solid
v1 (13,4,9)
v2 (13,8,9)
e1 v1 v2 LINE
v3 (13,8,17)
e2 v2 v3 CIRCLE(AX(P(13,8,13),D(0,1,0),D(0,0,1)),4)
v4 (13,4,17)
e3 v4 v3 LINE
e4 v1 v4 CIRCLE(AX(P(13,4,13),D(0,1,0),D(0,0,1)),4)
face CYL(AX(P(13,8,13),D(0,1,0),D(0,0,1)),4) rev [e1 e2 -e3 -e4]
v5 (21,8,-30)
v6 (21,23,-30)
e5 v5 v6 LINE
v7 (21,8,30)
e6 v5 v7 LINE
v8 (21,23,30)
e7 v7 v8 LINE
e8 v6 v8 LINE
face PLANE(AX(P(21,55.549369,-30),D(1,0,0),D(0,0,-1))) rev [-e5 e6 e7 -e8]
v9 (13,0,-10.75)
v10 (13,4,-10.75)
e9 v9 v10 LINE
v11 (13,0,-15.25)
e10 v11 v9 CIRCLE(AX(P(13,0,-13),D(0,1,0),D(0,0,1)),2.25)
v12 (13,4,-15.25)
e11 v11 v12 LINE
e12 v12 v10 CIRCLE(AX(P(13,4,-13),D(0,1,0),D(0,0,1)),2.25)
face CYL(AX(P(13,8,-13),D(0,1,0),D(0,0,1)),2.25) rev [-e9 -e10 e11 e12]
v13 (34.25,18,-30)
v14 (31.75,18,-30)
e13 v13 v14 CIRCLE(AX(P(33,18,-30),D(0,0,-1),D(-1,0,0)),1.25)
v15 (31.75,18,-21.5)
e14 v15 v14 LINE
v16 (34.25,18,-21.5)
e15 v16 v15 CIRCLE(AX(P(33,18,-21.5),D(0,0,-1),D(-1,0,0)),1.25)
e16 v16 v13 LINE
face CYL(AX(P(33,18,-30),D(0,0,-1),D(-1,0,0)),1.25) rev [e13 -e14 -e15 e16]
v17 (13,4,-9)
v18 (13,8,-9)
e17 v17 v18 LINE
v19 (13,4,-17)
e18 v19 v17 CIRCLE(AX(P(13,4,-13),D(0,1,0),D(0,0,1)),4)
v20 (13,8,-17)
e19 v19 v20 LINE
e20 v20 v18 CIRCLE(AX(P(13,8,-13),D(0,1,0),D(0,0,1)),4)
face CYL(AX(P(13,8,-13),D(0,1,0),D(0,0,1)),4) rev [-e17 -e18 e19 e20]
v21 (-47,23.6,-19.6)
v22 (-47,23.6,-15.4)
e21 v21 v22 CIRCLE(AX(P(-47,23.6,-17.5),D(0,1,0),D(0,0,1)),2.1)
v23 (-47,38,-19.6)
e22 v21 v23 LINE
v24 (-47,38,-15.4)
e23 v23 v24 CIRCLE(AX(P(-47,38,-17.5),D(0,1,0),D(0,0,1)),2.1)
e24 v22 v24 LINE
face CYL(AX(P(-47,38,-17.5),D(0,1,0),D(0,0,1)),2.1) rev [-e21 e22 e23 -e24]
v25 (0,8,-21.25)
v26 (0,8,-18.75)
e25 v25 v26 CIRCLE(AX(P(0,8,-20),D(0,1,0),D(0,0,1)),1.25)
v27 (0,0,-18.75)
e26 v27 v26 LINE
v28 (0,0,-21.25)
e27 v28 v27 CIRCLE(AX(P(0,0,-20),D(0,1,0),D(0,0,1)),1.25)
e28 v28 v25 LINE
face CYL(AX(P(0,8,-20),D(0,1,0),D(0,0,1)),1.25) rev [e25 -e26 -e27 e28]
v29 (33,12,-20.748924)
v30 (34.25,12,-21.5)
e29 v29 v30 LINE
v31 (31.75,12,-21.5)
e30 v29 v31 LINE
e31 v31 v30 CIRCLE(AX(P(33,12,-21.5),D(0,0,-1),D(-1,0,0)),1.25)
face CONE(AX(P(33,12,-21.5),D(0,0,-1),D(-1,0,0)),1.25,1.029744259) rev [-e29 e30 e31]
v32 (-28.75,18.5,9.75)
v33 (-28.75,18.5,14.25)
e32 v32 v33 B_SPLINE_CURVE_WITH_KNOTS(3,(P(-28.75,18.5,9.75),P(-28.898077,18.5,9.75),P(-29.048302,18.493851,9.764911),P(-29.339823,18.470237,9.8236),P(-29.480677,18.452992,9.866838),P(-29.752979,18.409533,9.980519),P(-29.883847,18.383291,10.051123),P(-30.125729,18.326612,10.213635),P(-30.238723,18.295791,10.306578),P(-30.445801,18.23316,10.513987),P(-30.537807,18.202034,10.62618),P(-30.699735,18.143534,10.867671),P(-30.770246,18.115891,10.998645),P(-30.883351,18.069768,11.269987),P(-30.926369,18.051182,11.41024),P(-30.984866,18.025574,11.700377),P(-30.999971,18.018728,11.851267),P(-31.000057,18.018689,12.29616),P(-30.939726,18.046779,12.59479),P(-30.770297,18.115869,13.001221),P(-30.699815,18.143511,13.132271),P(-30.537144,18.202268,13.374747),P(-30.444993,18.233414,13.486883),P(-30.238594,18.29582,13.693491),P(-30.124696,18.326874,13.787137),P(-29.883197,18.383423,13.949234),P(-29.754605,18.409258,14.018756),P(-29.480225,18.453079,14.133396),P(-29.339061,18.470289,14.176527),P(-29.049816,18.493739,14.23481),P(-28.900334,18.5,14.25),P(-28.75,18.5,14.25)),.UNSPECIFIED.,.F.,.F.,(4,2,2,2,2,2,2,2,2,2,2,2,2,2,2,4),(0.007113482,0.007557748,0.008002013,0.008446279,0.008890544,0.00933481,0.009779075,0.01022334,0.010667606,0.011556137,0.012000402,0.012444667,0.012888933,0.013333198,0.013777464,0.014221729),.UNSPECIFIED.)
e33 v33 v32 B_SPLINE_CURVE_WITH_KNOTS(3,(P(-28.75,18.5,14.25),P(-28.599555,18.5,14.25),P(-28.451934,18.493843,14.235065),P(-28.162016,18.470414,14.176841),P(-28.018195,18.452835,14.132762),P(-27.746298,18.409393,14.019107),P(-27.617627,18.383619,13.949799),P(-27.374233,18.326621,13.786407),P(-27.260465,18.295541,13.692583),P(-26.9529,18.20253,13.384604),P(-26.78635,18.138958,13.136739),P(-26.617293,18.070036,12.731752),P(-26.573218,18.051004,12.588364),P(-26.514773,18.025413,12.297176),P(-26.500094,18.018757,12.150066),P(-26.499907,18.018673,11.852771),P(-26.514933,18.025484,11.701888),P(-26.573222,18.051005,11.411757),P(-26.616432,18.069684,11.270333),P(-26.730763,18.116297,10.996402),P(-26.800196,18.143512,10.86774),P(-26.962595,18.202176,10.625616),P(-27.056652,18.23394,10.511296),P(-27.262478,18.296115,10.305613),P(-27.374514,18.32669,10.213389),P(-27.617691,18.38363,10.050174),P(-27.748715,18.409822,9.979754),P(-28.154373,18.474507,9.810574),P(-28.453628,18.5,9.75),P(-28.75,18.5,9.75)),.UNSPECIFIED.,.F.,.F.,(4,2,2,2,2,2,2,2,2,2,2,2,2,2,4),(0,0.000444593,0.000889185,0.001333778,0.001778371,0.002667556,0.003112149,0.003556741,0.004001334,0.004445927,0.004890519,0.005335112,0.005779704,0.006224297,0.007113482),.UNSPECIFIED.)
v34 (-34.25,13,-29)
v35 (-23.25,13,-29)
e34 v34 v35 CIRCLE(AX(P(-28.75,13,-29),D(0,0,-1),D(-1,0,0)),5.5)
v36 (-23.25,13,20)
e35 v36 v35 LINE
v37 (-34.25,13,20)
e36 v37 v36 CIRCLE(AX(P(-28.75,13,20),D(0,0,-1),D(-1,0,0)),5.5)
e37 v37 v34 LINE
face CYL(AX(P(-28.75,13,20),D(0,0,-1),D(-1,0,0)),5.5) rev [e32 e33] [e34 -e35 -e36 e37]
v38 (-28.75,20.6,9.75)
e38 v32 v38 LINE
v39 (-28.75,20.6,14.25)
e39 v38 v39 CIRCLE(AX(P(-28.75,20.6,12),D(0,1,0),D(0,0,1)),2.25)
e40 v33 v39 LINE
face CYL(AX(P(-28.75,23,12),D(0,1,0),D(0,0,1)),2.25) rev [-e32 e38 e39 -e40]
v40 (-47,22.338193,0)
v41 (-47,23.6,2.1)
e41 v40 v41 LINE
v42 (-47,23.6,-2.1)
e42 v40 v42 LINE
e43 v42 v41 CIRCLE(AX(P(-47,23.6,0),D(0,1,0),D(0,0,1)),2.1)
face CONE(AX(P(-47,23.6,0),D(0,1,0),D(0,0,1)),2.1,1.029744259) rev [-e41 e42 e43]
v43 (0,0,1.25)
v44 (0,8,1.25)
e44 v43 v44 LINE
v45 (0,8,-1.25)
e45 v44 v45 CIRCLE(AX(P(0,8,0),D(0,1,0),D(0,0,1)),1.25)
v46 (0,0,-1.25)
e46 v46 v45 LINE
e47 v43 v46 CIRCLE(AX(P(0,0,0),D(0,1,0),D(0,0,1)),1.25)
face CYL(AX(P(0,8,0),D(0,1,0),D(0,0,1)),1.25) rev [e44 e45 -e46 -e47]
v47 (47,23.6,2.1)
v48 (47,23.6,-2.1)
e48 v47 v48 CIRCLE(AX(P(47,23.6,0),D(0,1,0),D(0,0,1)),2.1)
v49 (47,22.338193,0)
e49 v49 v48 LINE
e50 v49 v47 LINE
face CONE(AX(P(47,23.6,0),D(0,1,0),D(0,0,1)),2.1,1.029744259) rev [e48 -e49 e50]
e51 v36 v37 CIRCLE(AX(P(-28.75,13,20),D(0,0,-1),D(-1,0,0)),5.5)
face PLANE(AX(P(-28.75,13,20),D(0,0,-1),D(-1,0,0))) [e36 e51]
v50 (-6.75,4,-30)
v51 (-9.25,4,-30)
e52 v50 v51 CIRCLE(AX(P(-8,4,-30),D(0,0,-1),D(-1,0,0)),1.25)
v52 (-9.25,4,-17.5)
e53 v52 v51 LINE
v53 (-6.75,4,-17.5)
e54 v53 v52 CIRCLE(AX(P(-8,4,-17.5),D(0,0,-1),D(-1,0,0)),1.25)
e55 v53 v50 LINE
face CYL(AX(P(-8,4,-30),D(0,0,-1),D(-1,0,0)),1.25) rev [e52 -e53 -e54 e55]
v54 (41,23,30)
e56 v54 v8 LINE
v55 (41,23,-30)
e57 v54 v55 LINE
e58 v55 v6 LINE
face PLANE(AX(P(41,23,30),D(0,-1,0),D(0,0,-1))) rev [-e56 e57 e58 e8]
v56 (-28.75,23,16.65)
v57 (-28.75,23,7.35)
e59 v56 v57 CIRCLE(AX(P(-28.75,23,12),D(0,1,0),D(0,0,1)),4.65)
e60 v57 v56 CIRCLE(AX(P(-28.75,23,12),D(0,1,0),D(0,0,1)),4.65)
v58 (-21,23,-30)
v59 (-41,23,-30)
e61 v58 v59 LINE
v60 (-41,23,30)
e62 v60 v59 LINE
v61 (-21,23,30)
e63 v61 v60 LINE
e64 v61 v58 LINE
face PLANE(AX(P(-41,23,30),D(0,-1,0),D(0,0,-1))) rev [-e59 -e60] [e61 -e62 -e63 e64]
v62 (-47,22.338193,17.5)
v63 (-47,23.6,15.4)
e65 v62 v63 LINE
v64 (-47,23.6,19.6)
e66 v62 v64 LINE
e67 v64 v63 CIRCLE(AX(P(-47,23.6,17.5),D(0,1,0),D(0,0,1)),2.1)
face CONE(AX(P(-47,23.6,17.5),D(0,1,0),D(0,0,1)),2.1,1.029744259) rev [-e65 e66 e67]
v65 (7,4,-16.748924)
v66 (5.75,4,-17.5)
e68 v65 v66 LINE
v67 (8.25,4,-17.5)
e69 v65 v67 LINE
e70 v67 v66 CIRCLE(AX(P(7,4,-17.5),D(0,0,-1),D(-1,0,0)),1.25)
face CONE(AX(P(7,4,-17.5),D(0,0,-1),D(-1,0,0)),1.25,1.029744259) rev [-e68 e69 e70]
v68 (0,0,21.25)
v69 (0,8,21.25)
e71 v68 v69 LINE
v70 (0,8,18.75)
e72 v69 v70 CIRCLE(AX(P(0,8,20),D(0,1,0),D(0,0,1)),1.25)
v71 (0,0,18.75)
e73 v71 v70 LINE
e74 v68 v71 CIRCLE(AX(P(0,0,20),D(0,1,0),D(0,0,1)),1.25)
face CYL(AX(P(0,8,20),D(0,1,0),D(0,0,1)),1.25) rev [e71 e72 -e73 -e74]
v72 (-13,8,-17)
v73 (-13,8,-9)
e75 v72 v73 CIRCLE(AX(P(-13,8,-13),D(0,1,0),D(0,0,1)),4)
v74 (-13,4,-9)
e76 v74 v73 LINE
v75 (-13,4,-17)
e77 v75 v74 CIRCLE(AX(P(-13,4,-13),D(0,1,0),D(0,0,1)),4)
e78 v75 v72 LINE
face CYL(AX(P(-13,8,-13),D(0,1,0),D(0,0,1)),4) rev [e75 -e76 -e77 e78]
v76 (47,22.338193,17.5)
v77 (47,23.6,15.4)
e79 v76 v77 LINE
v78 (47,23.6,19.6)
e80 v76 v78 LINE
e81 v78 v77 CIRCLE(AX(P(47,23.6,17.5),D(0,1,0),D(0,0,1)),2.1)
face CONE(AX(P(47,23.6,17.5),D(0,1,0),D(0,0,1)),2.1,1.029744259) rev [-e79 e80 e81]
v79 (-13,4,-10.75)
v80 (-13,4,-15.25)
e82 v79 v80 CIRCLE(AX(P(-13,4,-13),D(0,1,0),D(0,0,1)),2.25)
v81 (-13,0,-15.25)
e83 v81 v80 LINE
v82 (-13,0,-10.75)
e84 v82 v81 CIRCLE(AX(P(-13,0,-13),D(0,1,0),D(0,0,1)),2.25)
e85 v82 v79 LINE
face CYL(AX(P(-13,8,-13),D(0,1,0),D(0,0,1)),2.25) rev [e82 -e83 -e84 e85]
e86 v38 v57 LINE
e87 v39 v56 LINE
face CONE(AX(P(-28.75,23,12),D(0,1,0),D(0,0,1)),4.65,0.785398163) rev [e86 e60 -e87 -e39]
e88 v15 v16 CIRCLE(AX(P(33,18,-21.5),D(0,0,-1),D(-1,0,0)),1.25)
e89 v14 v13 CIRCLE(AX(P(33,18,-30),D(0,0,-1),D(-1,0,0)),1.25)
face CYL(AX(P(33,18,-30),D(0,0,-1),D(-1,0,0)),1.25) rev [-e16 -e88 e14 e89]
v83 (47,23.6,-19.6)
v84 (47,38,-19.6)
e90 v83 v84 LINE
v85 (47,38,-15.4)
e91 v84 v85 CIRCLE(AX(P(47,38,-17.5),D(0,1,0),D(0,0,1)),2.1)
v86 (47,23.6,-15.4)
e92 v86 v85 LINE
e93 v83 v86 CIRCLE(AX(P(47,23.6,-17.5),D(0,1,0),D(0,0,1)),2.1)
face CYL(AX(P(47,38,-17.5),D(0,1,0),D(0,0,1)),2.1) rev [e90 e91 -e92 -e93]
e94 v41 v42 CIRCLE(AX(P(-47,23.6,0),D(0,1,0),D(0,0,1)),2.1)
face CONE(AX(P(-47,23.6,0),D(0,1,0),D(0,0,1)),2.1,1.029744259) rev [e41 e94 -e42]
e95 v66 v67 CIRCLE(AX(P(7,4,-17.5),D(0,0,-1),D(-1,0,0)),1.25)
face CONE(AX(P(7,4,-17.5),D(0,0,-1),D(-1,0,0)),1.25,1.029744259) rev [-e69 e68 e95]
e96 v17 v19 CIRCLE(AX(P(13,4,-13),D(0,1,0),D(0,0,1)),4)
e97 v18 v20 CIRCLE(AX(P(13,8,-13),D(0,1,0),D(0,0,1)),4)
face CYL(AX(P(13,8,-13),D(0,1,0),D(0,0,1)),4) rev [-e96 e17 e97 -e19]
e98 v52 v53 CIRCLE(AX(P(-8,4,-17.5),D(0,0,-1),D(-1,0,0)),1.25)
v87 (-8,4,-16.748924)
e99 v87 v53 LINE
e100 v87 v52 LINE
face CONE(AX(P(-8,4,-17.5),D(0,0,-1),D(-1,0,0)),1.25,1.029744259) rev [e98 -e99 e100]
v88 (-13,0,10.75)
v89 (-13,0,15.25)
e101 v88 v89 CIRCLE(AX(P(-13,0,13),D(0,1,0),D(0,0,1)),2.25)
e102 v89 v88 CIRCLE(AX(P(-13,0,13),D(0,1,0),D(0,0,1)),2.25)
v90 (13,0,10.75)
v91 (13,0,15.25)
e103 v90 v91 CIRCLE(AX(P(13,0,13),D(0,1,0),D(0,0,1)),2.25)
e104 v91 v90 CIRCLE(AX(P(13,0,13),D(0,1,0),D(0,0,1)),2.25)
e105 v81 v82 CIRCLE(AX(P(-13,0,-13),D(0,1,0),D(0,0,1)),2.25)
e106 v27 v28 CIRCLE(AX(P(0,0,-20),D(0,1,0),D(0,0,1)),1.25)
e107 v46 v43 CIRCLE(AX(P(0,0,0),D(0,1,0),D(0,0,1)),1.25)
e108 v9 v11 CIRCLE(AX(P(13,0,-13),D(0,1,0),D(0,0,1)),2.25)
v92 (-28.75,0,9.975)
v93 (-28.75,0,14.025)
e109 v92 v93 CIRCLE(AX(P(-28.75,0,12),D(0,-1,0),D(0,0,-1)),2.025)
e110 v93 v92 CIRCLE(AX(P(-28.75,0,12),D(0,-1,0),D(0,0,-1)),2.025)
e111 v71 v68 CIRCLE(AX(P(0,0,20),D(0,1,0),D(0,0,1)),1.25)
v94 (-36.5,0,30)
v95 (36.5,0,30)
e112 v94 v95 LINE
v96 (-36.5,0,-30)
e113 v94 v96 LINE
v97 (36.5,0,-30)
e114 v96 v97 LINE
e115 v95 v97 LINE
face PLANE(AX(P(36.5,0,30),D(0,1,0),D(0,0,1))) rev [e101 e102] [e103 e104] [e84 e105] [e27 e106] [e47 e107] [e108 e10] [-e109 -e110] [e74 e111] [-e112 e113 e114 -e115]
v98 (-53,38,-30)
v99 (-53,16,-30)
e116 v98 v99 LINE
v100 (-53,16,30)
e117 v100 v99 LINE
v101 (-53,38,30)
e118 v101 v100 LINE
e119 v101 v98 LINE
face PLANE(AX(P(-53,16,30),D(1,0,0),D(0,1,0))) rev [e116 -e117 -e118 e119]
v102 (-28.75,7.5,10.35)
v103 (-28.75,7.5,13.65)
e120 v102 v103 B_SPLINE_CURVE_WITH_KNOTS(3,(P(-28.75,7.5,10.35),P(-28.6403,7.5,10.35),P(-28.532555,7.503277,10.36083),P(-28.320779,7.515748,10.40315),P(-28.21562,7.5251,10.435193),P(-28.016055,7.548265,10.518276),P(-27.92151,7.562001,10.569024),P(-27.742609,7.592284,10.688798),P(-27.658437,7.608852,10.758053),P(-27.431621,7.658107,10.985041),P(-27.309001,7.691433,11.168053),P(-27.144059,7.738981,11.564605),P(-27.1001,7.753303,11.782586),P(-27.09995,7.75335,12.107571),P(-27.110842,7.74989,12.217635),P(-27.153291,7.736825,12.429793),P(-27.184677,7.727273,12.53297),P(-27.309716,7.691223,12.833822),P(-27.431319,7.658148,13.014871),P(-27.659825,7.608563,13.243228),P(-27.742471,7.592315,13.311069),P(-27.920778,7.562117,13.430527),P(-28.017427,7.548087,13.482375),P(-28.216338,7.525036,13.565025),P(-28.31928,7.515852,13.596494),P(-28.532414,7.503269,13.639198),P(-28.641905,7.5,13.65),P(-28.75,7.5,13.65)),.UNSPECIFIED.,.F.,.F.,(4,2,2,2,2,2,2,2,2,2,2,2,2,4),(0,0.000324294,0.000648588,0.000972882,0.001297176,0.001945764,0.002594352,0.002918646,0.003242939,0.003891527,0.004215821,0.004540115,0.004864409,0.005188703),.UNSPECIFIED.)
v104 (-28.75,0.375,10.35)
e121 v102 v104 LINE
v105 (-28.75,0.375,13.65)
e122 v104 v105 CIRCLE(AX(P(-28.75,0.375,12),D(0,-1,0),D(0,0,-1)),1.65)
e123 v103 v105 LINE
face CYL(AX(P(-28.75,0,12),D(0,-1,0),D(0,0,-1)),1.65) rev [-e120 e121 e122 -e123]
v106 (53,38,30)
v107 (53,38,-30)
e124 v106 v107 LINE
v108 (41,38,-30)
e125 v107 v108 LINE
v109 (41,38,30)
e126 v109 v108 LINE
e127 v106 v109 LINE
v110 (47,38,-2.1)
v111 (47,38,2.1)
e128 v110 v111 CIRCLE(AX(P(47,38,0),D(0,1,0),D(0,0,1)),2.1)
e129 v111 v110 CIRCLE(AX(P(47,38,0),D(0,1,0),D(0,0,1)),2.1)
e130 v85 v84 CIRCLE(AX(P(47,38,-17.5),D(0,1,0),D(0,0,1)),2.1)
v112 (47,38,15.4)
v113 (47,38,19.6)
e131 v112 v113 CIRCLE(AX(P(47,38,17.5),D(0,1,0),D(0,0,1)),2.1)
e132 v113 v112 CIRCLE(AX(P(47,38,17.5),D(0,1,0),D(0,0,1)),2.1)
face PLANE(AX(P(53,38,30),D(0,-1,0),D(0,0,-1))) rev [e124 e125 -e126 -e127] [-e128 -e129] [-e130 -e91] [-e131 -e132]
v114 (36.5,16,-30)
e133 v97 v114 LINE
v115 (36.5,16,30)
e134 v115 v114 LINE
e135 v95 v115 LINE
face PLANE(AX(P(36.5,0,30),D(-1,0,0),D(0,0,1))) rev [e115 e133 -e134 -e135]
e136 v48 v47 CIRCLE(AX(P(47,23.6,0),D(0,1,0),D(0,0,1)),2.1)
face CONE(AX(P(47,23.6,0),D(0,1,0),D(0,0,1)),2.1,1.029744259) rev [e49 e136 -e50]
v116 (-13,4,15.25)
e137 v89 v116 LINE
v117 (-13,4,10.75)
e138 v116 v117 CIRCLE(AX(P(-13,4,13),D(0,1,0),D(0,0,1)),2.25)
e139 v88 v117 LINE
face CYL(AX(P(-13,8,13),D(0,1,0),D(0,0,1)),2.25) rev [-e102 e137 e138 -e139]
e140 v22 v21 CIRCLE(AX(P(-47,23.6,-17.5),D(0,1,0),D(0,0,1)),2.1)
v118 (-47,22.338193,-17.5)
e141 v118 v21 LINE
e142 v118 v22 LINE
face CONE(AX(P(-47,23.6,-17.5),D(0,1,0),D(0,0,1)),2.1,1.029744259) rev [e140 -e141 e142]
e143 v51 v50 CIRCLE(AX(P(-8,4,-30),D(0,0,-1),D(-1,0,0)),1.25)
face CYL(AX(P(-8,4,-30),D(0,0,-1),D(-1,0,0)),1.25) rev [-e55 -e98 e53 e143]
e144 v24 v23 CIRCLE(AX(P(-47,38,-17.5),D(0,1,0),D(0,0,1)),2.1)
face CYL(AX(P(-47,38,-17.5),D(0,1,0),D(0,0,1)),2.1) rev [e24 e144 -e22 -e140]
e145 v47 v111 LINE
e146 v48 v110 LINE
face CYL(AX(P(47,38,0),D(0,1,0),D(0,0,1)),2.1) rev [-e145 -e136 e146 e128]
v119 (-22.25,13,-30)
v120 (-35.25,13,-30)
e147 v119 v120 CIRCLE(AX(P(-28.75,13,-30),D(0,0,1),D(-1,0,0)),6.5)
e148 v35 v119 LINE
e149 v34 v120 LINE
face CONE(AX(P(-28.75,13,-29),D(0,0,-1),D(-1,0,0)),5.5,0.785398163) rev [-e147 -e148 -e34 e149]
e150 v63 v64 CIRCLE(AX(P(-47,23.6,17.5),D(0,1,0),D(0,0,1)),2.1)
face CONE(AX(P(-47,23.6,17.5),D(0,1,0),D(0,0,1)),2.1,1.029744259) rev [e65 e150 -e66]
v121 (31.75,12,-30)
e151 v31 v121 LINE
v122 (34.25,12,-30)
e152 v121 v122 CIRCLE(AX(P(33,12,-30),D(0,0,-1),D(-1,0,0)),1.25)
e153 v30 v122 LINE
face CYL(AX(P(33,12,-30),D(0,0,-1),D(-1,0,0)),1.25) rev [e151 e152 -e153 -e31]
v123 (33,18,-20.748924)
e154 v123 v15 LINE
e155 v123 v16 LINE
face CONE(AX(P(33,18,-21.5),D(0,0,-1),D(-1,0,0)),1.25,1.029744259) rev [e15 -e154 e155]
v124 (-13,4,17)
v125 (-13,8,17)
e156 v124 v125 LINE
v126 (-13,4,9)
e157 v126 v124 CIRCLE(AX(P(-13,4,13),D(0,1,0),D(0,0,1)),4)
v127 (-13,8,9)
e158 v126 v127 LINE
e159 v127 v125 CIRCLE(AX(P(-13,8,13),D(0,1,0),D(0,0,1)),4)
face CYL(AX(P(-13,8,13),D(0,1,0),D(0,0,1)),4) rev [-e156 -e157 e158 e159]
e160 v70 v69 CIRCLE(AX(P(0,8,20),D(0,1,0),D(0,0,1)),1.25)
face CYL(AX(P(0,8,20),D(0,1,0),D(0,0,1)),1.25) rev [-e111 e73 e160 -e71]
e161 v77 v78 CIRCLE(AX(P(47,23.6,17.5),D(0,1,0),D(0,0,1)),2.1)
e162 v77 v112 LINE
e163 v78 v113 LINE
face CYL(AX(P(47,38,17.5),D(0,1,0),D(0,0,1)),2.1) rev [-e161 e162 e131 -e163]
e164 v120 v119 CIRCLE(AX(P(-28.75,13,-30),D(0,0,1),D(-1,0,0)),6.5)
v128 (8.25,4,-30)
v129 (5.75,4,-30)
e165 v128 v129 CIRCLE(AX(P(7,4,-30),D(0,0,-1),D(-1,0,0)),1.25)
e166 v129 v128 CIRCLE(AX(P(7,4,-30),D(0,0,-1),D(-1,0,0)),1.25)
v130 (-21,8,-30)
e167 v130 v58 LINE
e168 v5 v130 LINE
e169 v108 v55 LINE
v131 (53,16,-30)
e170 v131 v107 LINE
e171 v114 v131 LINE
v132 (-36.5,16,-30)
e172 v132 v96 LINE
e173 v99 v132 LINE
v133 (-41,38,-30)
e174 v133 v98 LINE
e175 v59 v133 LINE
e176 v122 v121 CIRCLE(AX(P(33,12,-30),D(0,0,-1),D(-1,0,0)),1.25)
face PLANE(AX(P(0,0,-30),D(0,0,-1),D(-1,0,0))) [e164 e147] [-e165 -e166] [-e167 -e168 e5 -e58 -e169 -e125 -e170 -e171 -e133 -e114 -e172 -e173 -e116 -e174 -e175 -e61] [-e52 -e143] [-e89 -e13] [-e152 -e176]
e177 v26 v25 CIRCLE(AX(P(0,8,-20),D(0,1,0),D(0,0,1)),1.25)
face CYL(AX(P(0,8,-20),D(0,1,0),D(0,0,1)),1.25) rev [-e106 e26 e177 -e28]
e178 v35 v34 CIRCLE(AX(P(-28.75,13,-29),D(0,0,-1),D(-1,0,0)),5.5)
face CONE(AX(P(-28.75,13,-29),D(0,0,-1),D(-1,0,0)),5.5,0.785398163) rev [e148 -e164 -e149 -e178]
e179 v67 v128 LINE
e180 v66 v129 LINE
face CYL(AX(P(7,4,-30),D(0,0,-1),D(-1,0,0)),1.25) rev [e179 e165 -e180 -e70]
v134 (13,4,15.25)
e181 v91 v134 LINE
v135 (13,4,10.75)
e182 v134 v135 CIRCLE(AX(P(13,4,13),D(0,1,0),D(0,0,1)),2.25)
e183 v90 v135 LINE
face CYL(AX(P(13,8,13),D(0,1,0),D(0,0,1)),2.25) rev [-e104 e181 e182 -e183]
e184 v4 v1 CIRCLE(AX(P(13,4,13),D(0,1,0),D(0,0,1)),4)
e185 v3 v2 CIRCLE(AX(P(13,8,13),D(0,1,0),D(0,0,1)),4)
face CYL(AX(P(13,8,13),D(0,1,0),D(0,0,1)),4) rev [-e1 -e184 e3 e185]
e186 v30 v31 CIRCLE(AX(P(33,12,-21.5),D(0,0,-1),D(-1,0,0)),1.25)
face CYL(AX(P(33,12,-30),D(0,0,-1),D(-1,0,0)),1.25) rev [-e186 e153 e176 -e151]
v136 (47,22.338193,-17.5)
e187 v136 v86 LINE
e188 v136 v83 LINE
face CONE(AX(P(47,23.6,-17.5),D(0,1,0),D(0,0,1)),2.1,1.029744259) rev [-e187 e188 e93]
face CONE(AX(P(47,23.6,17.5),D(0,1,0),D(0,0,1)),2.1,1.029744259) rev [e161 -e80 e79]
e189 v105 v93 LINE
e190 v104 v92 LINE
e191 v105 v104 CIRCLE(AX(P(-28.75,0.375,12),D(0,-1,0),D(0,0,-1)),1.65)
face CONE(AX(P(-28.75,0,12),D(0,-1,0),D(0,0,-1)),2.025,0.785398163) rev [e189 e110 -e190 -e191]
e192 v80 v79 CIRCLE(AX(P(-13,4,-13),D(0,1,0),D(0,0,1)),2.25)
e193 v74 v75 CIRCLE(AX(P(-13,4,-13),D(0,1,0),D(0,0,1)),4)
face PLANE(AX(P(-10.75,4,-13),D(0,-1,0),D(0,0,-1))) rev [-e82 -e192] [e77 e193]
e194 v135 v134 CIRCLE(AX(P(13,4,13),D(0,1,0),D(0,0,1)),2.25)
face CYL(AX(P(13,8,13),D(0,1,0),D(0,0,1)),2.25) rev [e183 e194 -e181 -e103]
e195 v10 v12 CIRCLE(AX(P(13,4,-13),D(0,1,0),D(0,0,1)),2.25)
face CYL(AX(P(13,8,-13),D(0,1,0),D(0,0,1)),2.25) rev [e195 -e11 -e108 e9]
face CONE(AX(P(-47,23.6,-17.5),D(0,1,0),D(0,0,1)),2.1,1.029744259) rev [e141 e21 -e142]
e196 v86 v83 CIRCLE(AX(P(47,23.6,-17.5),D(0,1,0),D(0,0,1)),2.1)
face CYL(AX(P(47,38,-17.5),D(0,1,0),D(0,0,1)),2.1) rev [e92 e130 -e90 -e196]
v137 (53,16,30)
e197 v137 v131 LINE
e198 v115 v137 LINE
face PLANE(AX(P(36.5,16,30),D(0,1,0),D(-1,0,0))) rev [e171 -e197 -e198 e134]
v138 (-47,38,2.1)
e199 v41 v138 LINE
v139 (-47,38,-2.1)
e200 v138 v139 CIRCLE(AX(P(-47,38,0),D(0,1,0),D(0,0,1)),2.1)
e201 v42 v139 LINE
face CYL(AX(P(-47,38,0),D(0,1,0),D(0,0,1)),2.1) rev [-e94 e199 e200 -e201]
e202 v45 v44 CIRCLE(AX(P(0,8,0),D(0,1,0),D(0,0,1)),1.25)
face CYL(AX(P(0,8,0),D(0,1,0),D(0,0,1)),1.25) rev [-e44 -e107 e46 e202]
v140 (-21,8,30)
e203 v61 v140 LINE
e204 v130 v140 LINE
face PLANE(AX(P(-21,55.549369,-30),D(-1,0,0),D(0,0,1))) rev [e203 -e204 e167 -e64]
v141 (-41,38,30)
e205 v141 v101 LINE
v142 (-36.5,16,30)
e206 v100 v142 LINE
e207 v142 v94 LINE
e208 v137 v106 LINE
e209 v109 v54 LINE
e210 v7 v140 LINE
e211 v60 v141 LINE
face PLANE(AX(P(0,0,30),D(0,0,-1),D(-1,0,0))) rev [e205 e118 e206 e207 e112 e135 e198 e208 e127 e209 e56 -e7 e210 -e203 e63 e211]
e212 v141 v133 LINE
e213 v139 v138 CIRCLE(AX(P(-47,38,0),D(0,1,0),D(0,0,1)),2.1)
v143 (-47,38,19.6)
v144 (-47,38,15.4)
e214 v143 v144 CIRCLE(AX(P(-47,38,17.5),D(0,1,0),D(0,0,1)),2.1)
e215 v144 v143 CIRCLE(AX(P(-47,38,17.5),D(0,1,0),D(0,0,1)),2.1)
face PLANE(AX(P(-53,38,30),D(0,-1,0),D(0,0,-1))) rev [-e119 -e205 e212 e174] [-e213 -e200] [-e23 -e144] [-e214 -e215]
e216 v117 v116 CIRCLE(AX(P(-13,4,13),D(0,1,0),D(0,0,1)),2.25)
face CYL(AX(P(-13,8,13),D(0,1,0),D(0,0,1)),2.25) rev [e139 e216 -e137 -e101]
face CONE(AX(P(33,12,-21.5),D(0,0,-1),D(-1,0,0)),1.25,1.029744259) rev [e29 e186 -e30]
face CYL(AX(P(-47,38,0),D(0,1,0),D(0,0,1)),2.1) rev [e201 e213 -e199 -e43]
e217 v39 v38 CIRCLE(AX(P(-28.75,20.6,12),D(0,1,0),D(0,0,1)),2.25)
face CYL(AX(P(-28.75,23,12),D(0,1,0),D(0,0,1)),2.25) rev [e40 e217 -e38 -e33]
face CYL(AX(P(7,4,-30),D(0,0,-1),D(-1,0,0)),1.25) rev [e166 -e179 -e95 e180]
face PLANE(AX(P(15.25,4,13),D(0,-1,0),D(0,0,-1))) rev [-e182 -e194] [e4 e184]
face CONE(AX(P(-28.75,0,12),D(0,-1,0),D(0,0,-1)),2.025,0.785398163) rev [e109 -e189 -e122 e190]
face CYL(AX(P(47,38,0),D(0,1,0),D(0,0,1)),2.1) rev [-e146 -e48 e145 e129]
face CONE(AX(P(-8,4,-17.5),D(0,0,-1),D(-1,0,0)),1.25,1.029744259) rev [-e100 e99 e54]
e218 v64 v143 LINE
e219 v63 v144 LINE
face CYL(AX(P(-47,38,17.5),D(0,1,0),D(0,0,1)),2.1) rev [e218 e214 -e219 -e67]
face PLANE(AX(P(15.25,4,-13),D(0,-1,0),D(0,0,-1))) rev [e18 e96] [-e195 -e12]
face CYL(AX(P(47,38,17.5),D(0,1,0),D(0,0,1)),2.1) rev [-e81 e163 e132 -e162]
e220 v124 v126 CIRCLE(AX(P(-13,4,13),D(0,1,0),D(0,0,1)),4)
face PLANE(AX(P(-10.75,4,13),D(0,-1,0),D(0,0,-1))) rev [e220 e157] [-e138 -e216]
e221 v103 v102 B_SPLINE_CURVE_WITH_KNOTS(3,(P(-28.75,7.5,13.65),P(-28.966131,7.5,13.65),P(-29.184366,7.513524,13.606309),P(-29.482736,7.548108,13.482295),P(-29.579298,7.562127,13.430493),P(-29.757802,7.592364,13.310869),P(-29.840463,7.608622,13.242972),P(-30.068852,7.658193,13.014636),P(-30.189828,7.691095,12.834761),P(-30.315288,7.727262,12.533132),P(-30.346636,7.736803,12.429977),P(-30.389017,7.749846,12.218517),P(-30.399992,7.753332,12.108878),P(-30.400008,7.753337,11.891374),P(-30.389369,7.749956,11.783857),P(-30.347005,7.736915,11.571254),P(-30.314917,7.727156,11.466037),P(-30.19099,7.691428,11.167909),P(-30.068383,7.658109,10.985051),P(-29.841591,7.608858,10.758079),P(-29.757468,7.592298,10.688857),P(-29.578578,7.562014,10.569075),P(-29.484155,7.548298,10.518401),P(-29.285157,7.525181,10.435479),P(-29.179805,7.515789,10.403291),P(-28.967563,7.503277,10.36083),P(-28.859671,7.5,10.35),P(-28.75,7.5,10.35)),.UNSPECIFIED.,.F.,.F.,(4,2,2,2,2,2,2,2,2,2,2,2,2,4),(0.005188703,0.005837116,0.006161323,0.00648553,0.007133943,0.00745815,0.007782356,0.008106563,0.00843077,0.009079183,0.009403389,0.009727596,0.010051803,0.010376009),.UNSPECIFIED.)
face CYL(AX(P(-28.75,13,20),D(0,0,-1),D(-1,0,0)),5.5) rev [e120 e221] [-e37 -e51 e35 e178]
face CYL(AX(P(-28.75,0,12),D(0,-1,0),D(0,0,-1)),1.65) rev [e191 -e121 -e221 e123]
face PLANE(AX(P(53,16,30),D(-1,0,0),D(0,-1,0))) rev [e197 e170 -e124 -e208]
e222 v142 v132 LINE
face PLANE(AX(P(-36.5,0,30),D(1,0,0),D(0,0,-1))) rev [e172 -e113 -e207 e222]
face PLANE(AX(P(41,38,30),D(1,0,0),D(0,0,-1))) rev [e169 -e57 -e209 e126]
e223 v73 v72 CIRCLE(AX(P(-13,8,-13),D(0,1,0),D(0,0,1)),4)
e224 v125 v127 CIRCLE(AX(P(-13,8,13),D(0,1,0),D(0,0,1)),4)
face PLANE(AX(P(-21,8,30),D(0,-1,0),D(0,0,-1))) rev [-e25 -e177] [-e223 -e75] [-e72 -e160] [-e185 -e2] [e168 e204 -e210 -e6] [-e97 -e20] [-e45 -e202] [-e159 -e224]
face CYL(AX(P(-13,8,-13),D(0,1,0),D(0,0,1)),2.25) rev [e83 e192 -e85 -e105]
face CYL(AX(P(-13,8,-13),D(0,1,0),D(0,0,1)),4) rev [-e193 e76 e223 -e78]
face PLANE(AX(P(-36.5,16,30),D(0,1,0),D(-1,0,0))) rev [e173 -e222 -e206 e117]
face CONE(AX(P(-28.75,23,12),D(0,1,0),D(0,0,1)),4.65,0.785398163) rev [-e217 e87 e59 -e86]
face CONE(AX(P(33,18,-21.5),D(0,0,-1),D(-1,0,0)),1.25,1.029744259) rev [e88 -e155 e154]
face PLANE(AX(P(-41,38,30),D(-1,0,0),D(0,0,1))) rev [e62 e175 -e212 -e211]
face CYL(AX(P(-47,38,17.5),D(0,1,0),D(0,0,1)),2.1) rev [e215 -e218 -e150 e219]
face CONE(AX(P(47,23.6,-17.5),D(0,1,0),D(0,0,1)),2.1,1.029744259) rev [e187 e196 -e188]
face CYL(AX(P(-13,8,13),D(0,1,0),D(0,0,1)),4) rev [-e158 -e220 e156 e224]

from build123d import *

# Parameters (mm, degrees)
EXTRUDE_1_DEPTH              = 30
HOLE_WIZARD_M5_1_AT_2_COUNT  = 2
HOLE_WIZARD_M5_1_AT_2_PITCH  = 35
HOLE_WIZARD_M5_1_AT_3_COUNT  = 2
HOLE_WIZARD_M5_1_AT_3_PITCH  = 17.5
SKETCH_15_W                  = 50
SKETCH_15_H                  = 47.549368588
CUT_EXTRUDE_7_DEPTH          = 89.617154096
HOLE_WIZARD_2_D              = 4.5
HOLE_WIZARD_2_CBORE_D        = 8
HOLE_WIZARD_2_CBORE_DEPTH    = 4
HOLE_WIZARD_M3_4_D           = 2.5
HOLE_WIZARD_M3_4_DEPTH       = 12.5
HOLE_WIZARD_M3_4_TIP         = 0.751075774
HOLE_WIZARD_M3_5_D           = 2.5
PATTERN_LINEAR_1_COUNT       = 3
PATTERN_LINEAR_1_PITCH       = 20
HOLE_WIZARD_M3_6_D           = 2.5
HOLE_WIZARD_M3_6_DEPTH       = 8.5
HOLE_WIZARD_M3_6_TIP         = 0.751075774
MOVE_FACE_1_BY               = 4
MOVE_FACE_1_2_BY             = 4
SKETCH_37_R                  = 5.5
CUT_EXTRUDE_10_DEPTH         = 50
CHAMFER_2_SIZE               = 1
HOLE_WIZARD_1_D              = 4.5
HOLE_WIZARD_1_DEPTH          = 11.5
HOLE_WIZARD_1_CSINK_D        = 9.3
HOLE_WIZARD_1_CSINK_ANGLE    = 90
HOLE_WIZARD_1_TIP            = 1.351936393
SKETCH_38_R                  = 0.707693856
CUT_EXTRUDE_11_DEPTH         = 33
HOLE_WIZARD_M4_1_D           = 3.3
HOLE_WIZARD_M4_1_DEPTH       = 10.1
HOLE_WIZARD_M4_1_CSINK_D     = 4.05
HOLE_WIZARD_M4_1_CSINK_ANGLE = 90
HOLE_WIZARD_M4_1_TIP         = 0.991420021


with BuildPart() as part:
    # 草图1 → 凸台-拉伸1 (new, symmetric)
    with BuildSketch(Plane.XY):
        Polygon((36.5, 0), (-36.5, 0), (-36.5, 16), (-53, 16), (-53, 38), (-41, 38), (-41, 23), (-21, 23), (-21, 8), (21, 8), (21, 23), (41, 23), (41, 38), (53, 38), (53, 16), (36.5, 16), align=None)
    extrude(amount=EXTRUDE_1_DEPTH, both=True)

    # 草图9 → M5 螺纹孔1 (revolve, cut)
    with BuildSketch(Plane(origin=(-47, 38, -17.5), x_dir=(0, 0, 1), z_dir=(1, 0, 0))):
        Polygon((0, 0), (0, 15.6618073), (2.1, 14.4), (2.1, 0), align=None)
    hole_wizard_m5_1 = revolve(axis=Axis((-47, 44.35, -17.5), (0, -1, 0)), mode=Mode.SUBTRACT)

    # M5 螺纹孔1 at 2: M5 螺纹孔1 ×2
    with Locations(*[(0, 0, i * HOLE_WIZARD_M5_1_AT_2_PITCH) for i in range(1, HOLE_WIZARD_M5_1_AT_2_COUNT)]):
        add(hole_wizard_m5_1, mode=Mode.SUBTRACT)

    # M5 螺纹孔1 at 3: M5 螺纹孔1 ×2
    with Locations(*[(0, 0, i * HOLE_WIZARD_M5_1_AT_3_PITCH) for i in range(1, HOLE_WIZARD_M5_1_AT_3_COUNT)]):
        add(hole_wizard_m5_1, mode=Mode.SUBTRACT)

    # 镜向1: M5 螺纹孔1 across plane
    add(hole_wizard_m5_1.mirror(Plane(origin=(0, 0, 0), x_dir=(0, 0, 1), z_dir=(1, 0, 0))), mode=Mode.SUBTRACT)

    # 镜向1 copy 1 sketch → 镜向1 copy 1 (revolve, cut)
    with BuildSketch(Plane(origin=(47, 38, 17.5), x_dir=(0, 0, 1), z_dir=(-1, 0, 0))):
        Polygon((0, 0), (0, -15.6618073), (2.1, -14.4), (2.1, 0), align=None)
    revolve(axis=Axis((47, 44.35, 17.5), (0, 1, 0)), mode=Mode.SUBTRACT)

    # 镜向1 copy 2 sketch → 镜向1 copy 2 (revolve, cut)
    with BuildSketch(Plane(origin=(47, 38, 0), x_dir=(0, 0, 1), z_dir=(-1, 0, 0))):
        Polygon((0, 0), (0, -15.6618073), (2.1, -14.4), (2.1, 0), align=None)
    revolve(axis=Axis((47, 44.35, 0), (0, 1, 0)), mode=Mode.SUBTRACT)

    # 草图15 → 切除-拉伸7 (cut, through all)
    with BuildSketch(Plane.XY.offset(30)):
        with Locations((0, 31.774684294)):
            Rectangle(SKETCH_15_W, SKETCH_15_H)
    extrude(amount=-CUT_EXTRUDE_7_DEPTH, mode=Mode.SUBTRACT)

    # 打孔尺寸(%根据)开槽圆柱头螺钉的类型2 (through all)
    with Locations(Plane(origin=(0, 8, 0), x_dir=(1, 0, 0), z_dir=(0, 1, 0))):
        with Locations((-13, 13), (13, 13), (-13, -13), (13, -13)):
            CounterBoreHole(HOLE_WIZARD_2_D / 2, HOLE_WIZARD_2_CBORE_D / 2, HOLE_WIZARD_2_CBORE_DEPTH)

    # M3 螺纹孔4
    with Locations(Plane(origin=(0, 0, -30), x_dir=(-1, 0, 0), z_dir=(0, 0, -1))):
        with Locations((8, 4), (-7, 4)):
            Hole(HOLE_WIZARD_M3_4_D / 2, depth=HOLE_WIZARD_M3_4_DEPTH)
            with Locations((0, 0, -(HOLE_WIZARD_M3_4_DEPTH + HOLE_WIZARD_M3_4_TIP / 2))):  # 118° drill point
                Cone(0, HOLE_WIZARD_M3_4_D / 2, HOLE_WIZARD_M3_4_TIP, mode=Mode.SUBTRACT)

    # M3 螺纹孔5 (through all)
    with Locations(Plane(origin=(0, 8, 20), x_dir=(0, 0, 1), z_dir=(0, 1, 0))):
        with Locations((0, 0)):
            hole_wizard_m3_5 = Hole(HOLE_WIZARD_M3_5_D / 2)

    # 阵列(线性)1: M3 螺纹孔5 ×3
    with Locations(*[(0, 0, -i * PATTERN_LINEAR_1_PITCH) for i in range(1, PATTERN_LINEAR_1_COUNT)]):
        add(hole_wizard_m3_5, mode=Mode.SUBTRACT)

    # M3 螺纹孔6
    with Locations(Plane(origin=(33, 18, -30), x_dir=(-1, 0, 0), z_dir=(0, 0, -1))):
        with Locations((0, 0), (0, -6)):
            Hole(HOLE_WIZARD_M3_6_D / 2, depth=HOLE_WIZARD_M3_6_DEPTH)
            with Locations((0, 0, -(HOLE_WIZARD_M3_6_DEPTH + HOLE_WIZARD_M3_6_TIP / 2))):  # 118° drill point
                Cone(0, HOLE_WIZARD_M3_6_D / 2, HOLE_WIZARD_M3_6_TIP, mode=Mode.SUBTRACT)

    # Move Face 1: a face moved outward by 4.0
    extrude(part.faces().sort_by_distance((-25, 15.5, 0))[0], amount=MOVE_FACE_1_BY, dir=(1, 0, 0))

    # Move Face 1 2: a face moved outward by 4.0
    extrude(part.faces().sort_by_distance((25, 15.5, 0))[0], amount=MOVE_FACE_1_2_BY, dir=(-1, 0, 0))

    # 草图37 → 切除-拉伸10 (cut)
    with BuildSketch(Plane(origin=(0, 0, -30), x_dir=(-1, 0, 0), z_dir=(0, 0, -1))):
        with Locations((28.75, 13)):
            Circle(SKETCH_37_R)
    extrude(amount=-CUT_EXTRUDE_10_DEPTH, mode=Mode.SUBTRACT)

    # 倒角2
    chamfer_2_edges = [part.edges().sort_by_distance(p)[0] for p in [
        (-23.25, 13, -30),
    ]]
    chamfer(chamfer_2_edges, length=CHAMFER_2_SIZE)

    # 打孔尺寸(%根据)内六角花形半沉头螺钉的类型1
    with Locations(Plane(origin=(-28.75, 23, 12), x_dir=(0, 0, 1), z_dir=(0, 1, 0))):
        with Locations((0, 0)):
            CounterSinkHole(HOLE_WIZARD_1_D / 2, HOLE_WIZARD_1_CSINK_D / 2, depth=HOLE_WIZARD_1_DEPTH, counter_sink_angle=HOLE_WIZARD_1_CSINK_ANGLE)
            with Locations((0, 0, -(HOLE_WIZARD_1_DEPTH + HOLE_WIZARD_1_TIP / 2))):  # 118° drill point
                Cone(0, HOLE_WIZARD_1_D / 2, HOLE_WIZARD_1_TIP, mode=Mode.SUBTRACT)

    # 草图38 → 切除-拉伸11 (cut)
    with BuildSketch(Plane(origin=(0, 23, 0), x_dir=(1, 0, 0), z_dir=(0, 1, 0))):
        with Locations(Location((-28.75, -12, 0), (0, 0, 270))):
            Circle(SKETCH_38_R)
    extrude(amount=-CUT_EXTRUDE_11_DEPTH, mode=Mode.SUBTRACT)

    # M4 螺纹孔1
    with Locations(Plane(origin=(-28.75, 0, 12), x_dir=(0, 0, -1), z_dir=(0, -1, 0))):
        with Locations((0, 0)):
            CounterSinkHole(HOLE_WIZARD_M4_1_D / 2, HOLE_WIZARD_M4_1_CSINK_D / 2, depth=HOLE_WIZARD_M4_1_DEPTH, counter_sink_angle=HOLE_WIZARD_M4_1_CSINK_ANGLE)
            with Locations((0, 0, -(HOLE_WIZARD_M4_1_DEPTH + HOLE_WIZARD_M4_1_TIP / 2))):  # 118° drill point
                Cone(0, HOLE_WIZARD_M4_1_D / 2, HOLE_WIZARD_M4_1_TIP, mode=Mode.SUBTRACT)


solid = part.part
